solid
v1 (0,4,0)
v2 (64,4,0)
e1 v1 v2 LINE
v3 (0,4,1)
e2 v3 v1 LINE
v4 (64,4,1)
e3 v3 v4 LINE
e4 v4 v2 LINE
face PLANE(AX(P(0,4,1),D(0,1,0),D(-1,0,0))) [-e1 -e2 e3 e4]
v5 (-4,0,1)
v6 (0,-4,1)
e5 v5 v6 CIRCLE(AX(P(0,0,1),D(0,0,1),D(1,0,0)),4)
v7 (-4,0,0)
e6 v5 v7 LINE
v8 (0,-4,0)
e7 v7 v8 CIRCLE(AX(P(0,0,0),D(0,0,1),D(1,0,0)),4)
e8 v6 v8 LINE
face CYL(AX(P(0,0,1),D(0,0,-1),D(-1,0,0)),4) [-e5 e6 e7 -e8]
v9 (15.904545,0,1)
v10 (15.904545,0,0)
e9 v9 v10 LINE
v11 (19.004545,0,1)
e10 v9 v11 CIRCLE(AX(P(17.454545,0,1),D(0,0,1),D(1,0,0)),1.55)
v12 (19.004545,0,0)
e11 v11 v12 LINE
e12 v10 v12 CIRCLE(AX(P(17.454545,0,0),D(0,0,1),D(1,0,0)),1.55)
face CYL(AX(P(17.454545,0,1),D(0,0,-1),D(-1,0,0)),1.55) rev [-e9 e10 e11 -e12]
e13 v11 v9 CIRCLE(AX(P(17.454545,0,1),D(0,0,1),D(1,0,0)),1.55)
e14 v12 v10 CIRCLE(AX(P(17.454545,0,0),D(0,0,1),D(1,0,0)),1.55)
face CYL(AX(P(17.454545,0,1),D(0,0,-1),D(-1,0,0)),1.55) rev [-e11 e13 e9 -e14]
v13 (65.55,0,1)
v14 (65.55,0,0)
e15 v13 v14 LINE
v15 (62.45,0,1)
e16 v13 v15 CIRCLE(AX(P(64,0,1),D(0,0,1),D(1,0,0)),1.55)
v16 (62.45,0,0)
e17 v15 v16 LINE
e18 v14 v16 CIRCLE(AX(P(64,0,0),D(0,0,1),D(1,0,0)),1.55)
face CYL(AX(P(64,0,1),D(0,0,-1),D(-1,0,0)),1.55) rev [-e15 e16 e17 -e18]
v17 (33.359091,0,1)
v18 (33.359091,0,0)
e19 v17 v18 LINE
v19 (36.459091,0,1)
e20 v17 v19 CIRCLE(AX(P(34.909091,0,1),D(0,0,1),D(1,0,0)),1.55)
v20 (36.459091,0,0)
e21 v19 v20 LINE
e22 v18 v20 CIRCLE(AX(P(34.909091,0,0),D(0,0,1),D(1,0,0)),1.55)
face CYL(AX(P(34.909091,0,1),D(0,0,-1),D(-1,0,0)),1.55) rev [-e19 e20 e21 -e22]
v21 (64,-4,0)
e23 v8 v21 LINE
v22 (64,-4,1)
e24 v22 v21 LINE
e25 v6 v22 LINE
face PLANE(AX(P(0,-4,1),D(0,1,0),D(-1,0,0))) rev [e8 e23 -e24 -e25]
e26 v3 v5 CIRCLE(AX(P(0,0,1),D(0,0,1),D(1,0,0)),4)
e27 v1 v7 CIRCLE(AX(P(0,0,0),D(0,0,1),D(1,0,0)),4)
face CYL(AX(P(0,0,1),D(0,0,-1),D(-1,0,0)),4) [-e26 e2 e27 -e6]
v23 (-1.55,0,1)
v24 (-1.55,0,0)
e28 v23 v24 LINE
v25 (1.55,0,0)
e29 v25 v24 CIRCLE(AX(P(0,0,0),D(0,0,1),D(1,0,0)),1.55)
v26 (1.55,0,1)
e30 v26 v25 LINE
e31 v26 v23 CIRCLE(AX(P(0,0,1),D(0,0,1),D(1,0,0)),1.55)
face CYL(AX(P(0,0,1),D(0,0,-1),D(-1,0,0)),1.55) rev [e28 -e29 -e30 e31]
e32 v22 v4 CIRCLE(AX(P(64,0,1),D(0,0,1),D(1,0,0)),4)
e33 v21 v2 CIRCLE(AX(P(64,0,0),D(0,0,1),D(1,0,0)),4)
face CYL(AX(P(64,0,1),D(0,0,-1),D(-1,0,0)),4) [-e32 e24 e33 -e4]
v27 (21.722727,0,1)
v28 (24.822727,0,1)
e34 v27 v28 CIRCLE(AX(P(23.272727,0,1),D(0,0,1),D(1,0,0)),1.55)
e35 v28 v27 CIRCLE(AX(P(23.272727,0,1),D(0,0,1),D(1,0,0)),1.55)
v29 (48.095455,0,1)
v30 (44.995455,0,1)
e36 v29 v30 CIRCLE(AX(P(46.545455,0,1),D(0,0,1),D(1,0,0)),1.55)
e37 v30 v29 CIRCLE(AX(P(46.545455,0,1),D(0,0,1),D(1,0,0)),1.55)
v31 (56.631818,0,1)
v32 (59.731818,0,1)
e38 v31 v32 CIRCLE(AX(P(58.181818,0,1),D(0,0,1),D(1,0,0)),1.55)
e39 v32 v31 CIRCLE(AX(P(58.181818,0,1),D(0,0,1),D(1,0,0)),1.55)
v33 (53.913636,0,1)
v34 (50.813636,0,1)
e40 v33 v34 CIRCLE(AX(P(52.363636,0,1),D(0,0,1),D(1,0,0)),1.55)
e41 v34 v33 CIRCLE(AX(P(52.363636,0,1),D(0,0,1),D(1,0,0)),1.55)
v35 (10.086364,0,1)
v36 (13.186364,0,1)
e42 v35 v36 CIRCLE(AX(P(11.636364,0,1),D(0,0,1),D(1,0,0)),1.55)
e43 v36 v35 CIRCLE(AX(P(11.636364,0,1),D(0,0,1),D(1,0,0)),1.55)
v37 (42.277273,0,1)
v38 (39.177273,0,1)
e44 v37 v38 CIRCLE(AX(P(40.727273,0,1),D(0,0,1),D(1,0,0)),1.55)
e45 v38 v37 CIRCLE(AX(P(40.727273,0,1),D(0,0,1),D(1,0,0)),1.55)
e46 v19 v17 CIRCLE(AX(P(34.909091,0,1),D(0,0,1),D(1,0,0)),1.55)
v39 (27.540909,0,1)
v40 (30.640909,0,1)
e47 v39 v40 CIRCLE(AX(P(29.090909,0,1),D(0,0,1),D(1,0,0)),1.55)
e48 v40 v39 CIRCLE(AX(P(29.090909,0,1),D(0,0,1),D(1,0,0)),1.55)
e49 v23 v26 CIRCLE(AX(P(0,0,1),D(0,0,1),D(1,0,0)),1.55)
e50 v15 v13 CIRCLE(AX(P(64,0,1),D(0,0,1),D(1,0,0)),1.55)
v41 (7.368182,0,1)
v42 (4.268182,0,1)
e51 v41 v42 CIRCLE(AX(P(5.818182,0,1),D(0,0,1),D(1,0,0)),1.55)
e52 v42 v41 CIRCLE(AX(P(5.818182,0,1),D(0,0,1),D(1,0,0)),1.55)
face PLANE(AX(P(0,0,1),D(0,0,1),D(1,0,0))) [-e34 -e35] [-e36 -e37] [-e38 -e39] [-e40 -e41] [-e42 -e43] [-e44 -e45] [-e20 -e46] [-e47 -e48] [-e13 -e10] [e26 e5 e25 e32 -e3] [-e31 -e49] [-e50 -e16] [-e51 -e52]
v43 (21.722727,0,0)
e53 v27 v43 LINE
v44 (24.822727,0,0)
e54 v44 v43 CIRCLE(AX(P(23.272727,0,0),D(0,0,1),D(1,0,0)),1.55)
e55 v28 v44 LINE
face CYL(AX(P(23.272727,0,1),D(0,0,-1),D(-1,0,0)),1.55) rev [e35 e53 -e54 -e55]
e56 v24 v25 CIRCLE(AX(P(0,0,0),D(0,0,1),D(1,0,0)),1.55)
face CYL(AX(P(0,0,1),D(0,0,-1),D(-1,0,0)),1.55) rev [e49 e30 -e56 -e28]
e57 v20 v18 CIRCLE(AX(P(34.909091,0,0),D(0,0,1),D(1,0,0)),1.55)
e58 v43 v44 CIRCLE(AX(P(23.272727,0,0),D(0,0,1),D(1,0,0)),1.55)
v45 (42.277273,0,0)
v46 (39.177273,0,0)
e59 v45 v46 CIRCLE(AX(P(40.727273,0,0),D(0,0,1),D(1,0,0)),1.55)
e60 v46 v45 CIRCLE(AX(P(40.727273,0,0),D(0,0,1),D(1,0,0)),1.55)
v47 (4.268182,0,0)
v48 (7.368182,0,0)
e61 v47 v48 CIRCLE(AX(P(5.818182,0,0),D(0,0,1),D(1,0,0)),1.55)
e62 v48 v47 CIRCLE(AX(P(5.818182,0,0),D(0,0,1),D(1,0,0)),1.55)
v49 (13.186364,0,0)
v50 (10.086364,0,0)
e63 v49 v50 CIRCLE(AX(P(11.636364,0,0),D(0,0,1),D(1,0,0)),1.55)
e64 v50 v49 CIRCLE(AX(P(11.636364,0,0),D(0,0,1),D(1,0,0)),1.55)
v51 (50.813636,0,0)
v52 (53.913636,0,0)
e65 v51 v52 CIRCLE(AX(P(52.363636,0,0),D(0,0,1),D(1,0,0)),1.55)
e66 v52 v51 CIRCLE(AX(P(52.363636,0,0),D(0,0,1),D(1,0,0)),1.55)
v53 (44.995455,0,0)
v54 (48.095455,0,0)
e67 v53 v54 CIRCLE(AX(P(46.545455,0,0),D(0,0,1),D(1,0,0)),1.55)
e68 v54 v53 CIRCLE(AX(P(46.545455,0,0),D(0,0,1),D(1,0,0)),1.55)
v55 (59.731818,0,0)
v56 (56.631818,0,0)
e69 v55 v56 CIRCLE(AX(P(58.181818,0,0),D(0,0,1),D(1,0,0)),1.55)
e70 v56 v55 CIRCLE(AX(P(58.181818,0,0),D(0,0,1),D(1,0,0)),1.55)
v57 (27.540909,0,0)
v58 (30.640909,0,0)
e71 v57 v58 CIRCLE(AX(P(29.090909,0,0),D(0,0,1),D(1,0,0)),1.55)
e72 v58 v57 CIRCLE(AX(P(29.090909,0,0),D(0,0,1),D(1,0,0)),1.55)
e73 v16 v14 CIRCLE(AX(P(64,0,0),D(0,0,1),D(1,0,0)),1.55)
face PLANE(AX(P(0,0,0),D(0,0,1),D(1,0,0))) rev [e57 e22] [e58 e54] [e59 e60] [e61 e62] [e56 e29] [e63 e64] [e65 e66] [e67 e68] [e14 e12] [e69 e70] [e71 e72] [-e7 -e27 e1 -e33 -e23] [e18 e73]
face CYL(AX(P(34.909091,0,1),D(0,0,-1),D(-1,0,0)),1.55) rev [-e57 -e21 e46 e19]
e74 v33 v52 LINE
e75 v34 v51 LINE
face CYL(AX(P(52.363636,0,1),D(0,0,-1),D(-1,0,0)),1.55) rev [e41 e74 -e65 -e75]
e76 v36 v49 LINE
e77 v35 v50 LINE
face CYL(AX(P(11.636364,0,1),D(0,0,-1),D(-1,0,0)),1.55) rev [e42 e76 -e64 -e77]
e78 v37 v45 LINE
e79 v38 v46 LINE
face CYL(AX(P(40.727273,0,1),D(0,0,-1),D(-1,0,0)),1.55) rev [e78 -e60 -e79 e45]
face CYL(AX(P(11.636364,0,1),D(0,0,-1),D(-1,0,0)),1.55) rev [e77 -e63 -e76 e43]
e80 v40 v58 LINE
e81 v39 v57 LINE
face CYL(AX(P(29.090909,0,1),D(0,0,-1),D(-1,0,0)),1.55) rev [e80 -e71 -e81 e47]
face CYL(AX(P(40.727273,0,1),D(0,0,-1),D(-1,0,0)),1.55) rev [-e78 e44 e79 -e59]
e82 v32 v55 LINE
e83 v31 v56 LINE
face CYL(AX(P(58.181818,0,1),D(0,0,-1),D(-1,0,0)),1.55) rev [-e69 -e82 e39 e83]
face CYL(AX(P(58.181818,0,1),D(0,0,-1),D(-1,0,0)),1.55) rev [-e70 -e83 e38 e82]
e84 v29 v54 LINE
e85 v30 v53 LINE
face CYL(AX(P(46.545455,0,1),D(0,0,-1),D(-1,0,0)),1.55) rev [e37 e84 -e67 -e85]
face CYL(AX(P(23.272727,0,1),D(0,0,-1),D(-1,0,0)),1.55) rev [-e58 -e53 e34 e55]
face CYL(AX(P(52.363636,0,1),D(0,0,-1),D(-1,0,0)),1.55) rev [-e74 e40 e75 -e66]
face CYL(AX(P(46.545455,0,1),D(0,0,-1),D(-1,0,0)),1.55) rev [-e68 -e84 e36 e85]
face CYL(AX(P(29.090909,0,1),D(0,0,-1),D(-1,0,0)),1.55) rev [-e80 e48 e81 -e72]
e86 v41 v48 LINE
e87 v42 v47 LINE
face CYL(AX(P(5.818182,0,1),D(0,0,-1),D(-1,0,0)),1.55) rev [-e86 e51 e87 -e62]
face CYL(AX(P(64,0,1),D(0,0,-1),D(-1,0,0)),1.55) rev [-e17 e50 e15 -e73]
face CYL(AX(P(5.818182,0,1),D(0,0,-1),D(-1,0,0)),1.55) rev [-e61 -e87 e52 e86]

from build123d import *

# Parameters (mm, degrees)
SKETCH_1_R      = 1.55
EXTRUDE_1_DEPTH = 1


with BuildPart() as part:
    # 草图1 → 凸台-拉伸1 (new body)
    with BuildSketch(Plane.XY):
        with BuildLine():
            Line((0, 4), (64, 4))
            ThreePointArc((64, 4), (68, 0), (64, -4))
            Line((64, -4), (0, -4))
            ThreePointArc((0, -4), (-4, 0), (0, 4))
        make_face()
        Circle(SKETCH_1_R, mode=Mode.SUBTRACT)
        with Locations((5.818181818, 0)):
            Circle(SKETCH_1_R, mode=Mode.SUBTRACT)
        with Locations((11.636363636, 0)):
            Circle(SKETCH_1_R, mode=Mode.SUBTRACT)
        with Locations((17.454545455, 0)):
            Circle(SKETCH_1_R, mode=Mode.SUBTRACT)
        with Locations((23.272727273, 0)):
            Circle(SKETCH_1_R, mode=Mode.SUBTRACT)
        with Locations((29.090909091, 0)):
            Circle(SKETCH_1_R, mode=Mode.SUBTRACT)
        with Locations((34.909090909, 0)):
            Circle(SKETCH_1_R, mode=Mode.SUBTRACT)
        with Locations((40.727272727, 0)):
            Circle(SKETCH_1_R, mode=Mode.SUBTRACT)
        with Locations((46.545454545, 0)):
            Circle(SKETCH_1_R, mode=Mode.SUBTRACT)
        with Locations((52.363636364, 0)):
            Circle(SKETCH_1_R, mode=Mode.SUBTRACT)
        with Locations((58.181818182, 0)):
            Circle(SKETCH_1_R, mode=Mode.SUBTRACT)
        with Locations((64, 0)):
            Circle(SKETCH_1_R, mode=Mode.SUBTRACT)
    extrude(amount=EXTRUDE_1_DEPTH)


solid = part.part
